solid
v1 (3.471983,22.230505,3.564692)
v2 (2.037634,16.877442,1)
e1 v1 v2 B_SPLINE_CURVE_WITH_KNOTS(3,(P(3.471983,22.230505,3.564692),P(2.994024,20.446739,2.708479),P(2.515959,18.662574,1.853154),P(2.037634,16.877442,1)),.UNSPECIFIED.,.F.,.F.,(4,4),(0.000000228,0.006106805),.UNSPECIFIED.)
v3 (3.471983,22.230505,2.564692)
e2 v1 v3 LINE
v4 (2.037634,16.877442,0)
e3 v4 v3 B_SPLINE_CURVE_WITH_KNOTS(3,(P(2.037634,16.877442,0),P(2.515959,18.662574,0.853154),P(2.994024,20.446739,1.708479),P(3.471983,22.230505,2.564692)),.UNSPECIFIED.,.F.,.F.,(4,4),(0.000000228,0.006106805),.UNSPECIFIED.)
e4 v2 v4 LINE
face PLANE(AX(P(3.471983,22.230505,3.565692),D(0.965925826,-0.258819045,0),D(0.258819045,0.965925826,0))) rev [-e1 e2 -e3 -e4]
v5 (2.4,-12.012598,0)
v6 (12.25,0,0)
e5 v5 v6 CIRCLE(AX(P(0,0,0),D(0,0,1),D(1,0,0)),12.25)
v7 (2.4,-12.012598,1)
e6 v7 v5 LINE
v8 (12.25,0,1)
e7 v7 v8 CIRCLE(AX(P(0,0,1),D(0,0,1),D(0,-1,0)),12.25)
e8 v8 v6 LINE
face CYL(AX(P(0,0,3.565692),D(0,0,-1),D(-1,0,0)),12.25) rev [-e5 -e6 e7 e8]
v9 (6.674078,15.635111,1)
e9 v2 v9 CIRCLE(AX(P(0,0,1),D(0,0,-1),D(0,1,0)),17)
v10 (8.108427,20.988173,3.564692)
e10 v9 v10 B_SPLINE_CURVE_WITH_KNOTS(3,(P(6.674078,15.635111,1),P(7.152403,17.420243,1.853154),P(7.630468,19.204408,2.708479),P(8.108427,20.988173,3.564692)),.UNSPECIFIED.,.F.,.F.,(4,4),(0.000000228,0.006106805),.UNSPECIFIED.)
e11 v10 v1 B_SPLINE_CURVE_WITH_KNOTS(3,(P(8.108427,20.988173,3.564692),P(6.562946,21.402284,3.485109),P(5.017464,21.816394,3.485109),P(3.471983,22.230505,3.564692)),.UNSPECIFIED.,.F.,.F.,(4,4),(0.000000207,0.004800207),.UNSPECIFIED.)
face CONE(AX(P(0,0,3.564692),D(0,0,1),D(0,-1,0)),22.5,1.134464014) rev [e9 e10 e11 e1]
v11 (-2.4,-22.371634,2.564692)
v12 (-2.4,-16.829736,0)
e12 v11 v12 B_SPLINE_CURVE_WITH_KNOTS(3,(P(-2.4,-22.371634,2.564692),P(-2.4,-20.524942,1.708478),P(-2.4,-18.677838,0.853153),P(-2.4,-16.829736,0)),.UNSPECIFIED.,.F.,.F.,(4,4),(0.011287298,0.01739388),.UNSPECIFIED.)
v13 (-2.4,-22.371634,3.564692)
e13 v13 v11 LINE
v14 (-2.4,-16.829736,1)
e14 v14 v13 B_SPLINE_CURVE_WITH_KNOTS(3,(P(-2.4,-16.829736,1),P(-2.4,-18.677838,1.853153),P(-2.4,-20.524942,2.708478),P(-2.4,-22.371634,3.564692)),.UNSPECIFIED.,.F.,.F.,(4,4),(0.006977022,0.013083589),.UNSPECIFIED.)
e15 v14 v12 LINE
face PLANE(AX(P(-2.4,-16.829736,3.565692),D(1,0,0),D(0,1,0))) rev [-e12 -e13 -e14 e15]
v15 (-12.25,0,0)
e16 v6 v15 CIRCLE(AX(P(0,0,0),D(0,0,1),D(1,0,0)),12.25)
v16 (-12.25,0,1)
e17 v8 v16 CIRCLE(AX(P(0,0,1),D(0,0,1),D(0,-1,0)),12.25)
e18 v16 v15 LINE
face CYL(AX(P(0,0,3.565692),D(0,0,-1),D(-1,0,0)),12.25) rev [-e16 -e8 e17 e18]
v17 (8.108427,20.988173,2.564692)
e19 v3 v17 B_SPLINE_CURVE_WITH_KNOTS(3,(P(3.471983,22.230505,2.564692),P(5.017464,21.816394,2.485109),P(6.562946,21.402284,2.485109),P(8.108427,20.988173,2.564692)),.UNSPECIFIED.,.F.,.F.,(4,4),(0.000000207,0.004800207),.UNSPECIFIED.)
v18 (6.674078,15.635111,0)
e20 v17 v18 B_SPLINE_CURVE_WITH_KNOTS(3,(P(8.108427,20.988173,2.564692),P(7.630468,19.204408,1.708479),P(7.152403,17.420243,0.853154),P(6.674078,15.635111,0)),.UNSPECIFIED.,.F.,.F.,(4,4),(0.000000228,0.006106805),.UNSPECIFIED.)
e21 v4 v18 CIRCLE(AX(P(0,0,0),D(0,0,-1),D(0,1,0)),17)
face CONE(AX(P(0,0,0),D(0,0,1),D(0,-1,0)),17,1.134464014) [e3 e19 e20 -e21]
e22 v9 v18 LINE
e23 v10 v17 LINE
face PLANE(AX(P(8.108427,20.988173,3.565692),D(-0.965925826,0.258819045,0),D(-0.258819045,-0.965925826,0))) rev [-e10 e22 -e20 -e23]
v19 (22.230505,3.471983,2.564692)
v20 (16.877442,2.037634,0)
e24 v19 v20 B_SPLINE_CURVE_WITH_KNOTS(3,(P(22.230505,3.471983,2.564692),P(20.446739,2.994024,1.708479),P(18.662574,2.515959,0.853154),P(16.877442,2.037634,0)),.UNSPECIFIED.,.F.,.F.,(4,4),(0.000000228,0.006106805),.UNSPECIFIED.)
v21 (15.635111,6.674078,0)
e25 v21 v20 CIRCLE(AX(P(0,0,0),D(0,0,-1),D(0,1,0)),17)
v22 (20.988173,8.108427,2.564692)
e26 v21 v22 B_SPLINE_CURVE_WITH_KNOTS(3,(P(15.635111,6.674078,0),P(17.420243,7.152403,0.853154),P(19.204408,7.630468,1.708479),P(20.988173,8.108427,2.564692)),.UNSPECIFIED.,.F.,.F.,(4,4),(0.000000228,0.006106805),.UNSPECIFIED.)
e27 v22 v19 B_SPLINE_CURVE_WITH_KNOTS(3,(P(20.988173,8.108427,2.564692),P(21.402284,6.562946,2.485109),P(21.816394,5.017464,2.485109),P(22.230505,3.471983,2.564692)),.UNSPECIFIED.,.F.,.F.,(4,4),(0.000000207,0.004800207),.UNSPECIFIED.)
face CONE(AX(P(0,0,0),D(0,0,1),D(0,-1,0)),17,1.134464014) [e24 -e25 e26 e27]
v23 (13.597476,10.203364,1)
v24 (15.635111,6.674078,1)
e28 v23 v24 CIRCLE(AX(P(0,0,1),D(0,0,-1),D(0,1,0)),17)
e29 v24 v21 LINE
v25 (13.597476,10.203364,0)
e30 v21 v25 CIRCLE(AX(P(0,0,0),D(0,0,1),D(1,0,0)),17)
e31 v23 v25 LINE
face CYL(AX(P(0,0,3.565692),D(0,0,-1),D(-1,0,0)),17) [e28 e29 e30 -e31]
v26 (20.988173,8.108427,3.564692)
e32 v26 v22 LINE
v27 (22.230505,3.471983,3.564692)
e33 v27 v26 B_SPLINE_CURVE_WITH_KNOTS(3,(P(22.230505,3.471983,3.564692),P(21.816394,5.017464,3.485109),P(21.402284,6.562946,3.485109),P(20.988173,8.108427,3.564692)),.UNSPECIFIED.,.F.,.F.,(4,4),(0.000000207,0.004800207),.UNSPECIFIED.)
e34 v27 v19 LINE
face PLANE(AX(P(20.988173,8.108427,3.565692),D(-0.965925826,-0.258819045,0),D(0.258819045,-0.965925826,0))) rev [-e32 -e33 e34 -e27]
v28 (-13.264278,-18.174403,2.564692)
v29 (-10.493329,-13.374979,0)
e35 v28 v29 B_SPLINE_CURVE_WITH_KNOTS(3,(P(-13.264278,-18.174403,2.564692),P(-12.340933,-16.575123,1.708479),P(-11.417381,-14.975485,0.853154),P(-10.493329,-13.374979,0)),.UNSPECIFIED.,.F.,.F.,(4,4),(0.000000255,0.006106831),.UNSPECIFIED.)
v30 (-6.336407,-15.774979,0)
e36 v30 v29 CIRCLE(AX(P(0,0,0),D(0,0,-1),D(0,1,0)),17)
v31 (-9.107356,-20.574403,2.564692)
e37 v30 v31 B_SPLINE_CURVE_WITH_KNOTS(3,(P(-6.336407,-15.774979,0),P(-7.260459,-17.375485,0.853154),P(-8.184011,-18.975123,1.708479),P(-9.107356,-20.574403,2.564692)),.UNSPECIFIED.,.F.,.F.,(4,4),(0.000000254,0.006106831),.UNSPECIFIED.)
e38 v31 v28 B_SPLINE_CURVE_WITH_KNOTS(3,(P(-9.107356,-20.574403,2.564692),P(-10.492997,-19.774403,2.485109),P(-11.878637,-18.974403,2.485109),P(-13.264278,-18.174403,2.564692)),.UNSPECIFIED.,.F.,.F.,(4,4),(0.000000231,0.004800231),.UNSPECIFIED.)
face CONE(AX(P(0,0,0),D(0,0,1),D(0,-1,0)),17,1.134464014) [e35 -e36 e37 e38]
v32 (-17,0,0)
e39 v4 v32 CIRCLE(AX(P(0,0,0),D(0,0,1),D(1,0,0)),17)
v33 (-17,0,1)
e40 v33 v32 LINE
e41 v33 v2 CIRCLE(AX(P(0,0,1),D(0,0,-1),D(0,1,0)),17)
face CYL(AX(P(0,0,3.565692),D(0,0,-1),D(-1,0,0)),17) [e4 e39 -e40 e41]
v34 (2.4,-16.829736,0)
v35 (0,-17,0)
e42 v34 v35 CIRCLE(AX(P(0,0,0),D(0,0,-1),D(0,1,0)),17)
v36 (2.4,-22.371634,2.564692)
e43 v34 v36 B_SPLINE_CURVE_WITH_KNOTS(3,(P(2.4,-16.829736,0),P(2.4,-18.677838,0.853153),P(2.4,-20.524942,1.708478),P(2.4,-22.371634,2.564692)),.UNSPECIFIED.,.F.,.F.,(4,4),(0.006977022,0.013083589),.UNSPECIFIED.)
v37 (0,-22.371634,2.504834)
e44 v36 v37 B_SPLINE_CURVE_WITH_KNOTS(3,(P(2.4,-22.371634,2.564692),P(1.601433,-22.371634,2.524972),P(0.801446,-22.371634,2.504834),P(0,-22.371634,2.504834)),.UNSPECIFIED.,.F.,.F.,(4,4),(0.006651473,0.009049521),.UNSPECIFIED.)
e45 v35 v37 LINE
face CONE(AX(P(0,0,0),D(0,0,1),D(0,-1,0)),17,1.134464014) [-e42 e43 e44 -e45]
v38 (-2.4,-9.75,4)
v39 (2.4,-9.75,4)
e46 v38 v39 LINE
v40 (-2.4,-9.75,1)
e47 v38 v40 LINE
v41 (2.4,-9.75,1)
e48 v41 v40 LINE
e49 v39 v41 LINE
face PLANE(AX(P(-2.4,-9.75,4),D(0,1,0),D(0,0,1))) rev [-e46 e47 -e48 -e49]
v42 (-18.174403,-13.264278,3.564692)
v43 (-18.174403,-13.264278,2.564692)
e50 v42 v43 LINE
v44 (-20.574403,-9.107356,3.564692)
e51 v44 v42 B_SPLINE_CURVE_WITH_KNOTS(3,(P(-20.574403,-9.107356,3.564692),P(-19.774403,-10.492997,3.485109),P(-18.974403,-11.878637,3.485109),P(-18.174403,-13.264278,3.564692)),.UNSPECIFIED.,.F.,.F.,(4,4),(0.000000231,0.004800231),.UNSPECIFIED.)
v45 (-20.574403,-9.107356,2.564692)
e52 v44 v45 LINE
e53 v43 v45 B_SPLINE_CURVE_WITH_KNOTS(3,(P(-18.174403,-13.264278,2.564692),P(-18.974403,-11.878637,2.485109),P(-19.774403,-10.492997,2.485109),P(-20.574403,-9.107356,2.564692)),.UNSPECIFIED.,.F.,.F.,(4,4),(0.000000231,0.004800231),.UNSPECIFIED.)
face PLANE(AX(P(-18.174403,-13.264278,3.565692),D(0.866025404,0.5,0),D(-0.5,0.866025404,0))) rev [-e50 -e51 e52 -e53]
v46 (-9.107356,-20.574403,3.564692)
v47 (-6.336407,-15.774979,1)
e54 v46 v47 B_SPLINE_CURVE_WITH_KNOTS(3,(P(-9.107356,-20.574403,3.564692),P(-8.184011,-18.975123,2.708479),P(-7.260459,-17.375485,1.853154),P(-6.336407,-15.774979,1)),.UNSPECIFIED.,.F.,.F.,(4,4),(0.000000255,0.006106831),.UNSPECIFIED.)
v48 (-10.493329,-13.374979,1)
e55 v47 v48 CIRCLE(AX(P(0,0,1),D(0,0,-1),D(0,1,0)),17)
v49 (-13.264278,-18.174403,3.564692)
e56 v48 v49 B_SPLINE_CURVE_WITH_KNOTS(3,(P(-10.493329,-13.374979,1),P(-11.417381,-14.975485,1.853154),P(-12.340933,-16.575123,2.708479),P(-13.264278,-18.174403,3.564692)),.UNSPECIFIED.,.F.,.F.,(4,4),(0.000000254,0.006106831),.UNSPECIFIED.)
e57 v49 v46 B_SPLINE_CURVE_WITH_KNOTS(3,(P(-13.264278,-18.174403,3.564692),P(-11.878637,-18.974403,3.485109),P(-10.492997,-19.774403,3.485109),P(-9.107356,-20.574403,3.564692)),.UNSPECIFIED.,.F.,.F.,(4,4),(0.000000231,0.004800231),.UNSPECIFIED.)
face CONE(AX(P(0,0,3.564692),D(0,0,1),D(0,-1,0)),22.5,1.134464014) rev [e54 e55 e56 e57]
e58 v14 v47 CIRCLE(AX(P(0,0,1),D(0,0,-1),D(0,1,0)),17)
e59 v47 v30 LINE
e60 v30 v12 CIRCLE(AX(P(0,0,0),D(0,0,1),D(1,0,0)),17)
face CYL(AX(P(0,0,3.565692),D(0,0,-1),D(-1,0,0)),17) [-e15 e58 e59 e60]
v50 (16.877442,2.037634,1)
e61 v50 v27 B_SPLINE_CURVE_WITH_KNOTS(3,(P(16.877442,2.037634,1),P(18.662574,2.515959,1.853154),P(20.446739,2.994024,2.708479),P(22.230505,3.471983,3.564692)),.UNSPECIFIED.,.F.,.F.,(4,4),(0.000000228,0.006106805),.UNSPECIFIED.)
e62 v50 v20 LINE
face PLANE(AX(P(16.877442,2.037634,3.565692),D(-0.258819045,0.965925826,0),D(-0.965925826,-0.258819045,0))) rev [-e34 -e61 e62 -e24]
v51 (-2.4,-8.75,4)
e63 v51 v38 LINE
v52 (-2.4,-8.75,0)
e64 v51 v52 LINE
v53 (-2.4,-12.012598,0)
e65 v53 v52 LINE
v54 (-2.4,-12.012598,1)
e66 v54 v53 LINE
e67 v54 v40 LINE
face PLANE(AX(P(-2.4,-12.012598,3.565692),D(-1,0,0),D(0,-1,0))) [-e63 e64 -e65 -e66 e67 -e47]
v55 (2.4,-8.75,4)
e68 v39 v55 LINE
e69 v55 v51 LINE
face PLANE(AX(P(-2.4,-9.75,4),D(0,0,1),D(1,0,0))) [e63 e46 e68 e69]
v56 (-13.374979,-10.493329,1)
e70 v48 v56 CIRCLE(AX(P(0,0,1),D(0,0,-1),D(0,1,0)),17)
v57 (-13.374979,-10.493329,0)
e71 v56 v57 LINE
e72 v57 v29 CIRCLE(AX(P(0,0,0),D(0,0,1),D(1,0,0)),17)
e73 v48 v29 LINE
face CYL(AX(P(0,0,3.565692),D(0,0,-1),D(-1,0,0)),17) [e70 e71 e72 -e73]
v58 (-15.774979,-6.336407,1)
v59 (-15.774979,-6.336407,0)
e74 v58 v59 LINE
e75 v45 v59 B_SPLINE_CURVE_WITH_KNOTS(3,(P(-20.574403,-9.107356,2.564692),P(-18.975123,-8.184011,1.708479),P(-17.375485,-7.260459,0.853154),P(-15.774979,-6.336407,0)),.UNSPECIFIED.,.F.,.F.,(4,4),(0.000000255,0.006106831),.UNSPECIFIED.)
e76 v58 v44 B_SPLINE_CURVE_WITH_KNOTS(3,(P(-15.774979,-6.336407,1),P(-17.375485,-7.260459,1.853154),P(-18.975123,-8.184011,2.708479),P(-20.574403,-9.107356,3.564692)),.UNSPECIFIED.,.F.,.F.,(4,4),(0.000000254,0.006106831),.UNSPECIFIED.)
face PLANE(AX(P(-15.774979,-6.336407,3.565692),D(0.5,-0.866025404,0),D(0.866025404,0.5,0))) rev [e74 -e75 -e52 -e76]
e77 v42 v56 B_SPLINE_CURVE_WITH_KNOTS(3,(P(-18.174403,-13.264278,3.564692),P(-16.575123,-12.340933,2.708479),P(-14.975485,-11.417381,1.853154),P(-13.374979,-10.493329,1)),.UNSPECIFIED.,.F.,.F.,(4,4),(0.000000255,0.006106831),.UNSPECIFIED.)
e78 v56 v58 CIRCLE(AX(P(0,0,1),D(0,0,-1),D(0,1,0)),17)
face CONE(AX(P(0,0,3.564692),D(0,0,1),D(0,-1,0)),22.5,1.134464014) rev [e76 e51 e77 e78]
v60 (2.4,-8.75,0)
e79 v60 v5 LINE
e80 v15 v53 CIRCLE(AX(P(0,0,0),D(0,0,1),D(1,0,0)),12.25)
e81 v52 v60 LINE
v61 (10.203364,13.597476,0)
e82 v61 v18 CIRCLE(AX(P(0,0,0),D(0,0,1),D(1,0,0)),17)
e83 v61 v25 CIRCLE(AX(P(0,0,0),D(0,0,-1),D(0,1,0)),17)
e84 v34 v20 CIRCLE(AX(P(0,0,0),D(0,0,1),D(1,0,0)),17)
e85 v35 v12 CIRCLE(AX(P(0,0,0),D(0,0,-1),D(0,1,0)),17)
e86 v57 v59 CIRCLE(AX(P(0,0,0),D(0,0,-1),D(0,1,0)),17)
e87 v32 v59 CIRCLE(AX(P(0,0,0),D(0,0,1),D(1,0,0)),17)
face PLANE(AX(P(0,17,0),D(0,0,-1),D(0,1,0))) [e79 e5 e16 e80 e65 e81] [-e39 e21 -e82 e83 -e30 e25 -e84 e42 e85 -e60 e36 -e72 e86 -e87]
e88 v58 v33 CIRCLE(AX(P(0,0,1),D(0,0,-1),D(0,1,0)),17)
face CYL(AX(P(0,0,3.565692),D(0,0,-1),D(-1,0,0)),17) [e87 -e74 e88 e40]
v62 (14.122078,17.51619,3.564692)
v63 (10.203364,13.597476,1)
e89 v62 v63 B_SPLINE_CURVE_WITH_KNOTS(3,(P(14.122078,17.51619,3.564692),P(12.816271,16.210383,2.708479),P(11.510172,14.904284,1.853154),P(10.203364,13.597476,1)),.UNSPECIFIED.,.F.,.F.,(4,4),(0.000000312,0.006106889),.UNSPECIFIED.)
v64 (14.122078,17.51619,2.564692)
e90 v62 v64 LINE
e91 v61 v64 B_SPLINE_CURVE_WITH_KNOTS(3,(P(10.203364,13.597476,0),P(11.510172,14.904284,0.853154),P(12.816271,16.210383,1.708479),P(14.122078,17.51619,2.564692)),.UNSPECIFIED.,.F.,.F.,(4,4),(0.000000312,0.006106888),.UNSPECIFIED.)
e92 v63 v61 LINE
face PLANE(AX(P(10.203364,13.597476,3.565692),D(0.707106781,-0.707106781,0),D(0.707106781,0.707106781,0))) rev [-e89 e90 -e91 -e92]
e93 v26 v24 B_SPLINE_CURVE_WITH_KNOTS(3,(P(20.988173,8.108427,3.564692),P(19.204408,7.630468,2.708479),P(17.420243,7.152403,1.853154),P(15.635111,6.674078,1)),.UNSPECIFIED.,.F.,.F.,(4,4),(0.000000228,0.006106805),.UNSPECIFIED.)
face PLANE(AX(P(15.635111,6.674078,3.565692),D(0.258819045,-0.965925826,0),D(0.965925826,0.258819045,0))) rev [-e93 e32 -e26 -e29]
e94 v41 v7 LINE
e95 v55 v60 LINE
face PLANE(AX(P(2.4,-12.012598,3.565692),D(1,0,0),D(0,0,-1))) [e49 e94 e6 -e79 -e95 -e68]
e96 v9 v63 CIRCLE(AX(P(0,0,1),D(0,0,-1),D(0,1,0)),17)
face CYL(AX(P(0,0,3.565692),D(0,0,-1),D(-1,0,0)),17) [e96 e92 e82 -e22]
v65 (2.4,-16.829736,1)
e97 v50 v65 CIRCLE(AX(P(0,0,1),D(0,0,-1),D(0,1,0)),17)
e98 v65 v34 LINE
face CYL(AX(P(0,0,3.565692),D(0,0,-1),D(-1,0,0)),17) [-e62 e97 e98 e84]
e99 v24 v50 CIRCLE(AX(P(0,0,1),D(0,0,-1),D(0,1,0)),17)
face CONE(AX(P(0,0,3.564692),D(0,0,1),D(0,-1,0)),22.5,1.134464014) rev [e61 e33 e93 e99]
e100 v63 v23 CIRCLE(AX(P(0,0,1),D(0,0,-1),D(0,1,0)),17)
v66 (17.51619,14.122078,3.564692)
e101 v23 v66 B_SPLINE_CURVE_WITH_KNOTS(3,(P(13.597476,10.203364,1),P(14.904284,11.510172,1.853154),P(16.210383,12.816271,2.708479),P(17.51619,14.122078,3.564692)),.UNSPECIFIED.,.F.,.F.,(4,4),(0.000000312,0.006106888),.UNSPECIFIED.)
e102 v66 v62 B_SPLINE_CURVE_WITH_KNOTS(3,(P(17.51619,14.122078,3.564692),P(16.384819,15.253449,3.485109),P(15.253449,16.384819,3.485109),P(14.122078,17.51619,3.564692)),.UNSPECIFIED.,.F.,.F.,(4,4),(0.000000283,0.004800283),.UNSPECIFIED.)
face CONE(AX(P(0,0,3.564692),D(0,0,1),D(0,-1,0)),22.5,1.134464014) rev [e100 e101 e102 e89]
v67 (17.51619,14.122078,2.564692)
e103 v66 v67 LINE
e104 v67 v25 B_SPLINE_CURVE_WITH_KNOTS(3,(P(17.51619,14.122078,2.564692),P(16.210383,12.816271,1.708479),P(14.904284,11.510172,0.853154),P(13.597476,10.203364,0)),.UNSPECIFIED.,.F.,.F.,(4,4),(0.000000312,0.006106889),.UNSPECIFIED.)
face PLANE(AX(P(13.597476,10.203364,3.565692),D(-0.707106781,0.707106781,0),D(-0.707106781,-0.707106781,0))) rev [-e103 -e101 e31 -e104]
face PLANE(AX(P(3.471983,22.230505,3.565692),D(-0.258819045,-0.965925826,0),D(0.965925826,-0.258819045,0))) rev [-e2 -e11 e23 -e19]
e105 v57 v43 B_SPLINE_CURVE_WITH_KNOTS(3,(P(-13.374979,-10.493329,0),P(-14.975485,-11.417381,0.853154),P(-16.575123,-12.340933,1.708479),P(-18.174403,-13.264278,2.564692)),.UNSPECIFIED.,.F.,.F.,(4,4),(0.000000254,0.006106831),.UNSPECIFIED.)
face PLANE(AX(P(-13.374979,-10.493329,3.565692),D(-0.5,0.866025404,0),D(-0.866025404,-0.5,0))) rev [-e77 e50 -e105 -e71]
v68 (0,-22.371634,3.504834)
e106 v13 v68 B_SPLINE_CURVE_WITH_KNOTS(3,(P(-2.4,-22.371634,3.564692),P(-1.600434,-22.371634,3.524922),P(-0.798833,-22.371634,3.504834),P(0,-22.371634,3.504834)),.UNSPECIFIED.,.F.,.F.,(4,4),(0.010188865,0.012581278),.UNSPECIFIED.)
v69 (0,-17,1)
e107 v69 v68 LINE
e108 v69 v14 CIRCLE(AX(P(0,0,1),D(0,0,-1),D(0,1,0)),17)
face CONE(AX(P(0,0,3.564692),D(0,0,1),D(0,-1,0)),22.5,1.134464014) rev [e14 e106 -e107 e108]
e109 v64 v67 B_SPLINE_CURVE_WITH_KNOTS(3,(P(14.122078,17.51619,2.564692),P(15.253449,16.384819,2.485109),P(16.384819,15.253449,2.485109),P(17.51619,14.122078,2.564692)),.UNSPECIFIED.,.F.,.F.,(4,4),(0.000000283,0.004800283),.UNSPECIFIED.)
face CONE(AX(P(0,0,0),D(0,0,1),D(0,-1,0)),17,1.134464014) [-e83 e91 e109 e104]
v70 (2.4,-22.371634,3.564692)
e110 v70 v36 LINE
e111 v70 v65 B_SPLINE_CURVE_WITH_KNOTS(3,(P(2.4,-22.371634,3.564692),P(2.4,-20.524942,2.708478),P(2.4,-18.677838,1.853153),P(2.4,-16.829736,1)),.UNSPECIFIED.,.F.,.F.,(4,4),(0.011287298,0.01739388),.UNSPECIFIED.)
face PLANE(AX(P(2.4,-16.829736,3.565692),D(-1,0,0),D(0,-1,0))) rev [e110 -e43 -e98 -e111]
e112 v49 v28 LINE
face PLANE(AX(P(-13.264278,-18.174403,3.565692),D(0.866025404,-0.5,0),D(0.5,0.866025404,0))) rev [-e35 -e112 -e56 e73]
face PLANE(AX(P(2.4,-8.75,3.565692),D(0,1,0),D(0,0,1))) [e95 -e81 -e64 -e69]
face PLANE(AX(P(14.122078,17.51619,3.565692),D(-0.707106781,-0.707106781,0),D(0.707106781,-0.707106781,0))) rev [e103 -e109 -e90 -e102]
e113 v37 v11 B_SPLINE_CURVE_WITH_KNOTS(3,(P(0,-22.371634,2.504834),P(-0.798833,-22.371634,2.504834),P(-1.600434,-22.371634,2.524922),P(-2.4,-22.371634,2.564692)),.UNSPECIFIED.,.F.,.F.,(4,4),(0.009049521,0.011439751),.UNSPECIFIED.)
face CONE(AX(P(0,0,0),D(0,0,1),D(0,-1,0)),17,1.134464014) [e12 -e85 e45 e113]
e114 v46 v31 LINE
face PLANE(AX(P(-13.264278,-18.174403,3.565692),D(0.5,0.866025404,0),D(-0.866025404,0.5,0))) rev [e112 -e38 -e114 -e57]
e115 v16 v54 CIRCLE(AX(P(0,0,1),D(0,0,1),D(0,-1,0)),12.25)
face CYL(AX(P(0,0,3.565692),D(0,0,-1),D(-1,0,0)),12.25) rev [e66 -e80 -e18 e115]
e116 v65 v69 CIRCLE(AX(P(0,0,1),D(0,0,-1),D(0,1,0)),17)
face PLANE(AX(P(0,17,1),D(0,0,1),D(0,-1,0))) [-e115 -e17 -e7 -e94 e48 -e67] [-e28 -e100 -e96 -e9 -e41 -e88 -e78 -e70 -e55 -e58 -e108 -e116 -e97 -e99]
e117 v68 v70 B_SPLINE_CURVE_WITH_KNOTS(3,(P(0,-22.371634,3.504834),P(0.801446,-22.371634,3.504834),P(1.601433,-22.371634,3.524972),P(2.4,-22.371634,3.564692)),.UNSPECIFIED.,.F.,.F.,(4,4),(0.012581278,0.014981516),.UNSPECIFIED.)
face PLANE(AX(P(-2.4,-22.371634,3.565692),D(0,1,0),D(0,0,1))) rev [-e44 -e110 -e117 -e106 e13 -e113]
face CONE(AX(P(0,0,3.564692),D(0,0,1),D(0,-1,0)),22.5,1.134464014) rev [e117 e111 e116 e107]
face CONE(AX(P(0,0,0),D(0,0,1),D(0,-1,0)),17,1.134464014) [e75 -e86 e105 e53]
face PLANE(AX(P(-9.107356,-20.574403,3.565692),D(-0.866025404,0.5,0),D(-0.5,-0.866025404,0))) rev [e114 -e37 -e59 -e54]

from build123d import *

# Parameters (mm, degrees)
CUT_EXTRUDE2_START  = -3e-06
SKETCH3_OUTSIDE_W   = 59.748
SKETCH3_OUTSIDE_H   = 59.748
CUT_EXTRUDE2_DEPTH  = 3.564697
SKETCH4_W           = 4.8
SKETCH4_H           = 1
BOSS_EXTRUDE1_DEPTH = 4


with BuildPart() as part:
    # Sketch2 → Boss-Revolve (revolve)
    with BuildSketch(Plane(origin=(0, 0, 0), x_dir=(0, 0, -1), z_dir=(1, 0, 0))):
        Polygon((-2.56469212, 22.5), (0, 17), (0, 0), (-1, 0), (-1, 17), (-3.56469212, 22.5), align=None)
    revolve(axis=Axis((0, 0, 0), (0, 0, 1)))

    # Sketch3 outside → Cut-Extrude2 (cut)
    # profile 1 of 2: a face of its own
    with BuildSketch(Plane.XY.offset(CUT_EXTRUDE2_START)):
        Rectangle(SKETCH3_OUTSIDE_W, SKETCH3_OUTSIDE_H)
        with BuildLine():
            Line((-2.4, -16.829735589), (-2.4, -22.371633825))
            Line((-2.4, -22.371633825), (2.4, -22.371633825))
            Line((2.4, -22.371633825), (2.4, -16.829735589))
            ThreePointArc((2.4, -16.829735589), (13.487006785, -10.348944293), (16.877441963, 2.037634111))
            Line((16.877441963, 2.037634111), (22.230504596, 3.471982921))
            Line((22.230504596, 3.471982921), (20.98817318, 8.108426887))
            Line((20.98817318, 8.108426887), (15.635110547, 6.674078078))
            ThreePointArc((15.635110547, 6.674078078), (14.722431864, 8.5), (13.597476435, 10.203363886))
            Line((13.597476435, 10.203363886), (17.516190259, 14.122077709))
            Line((17.516190259, 14.122077709), (14.122077709, 17.516190259))
            Line((14.122077709, 17.516190259), (10.203363886, 13.597476435))
            ThreePointArc((10.203363886, 13.597476435), (8.5, 14.722431864), (6.674078078, 15.635110547))
            Line((6.674078078, 15.635110547), (8.108426887, 20.98817318))
            Line((8.108426887, 20.98817318), (3.471982921, 22.230504596))
            Line((3.471982921, 22.230504596), (2.037634111, 16.877441963))
            ThreePointArc((2.037634111, 16.877441963), (-13.487006785, 10.348944293), (-15.774978559, -6.336406825))
            Line((-15.774978559, -6.336406825), (-20.574403217, -9.107355943))
            Line((-20.574403217, -9.107355943), (-18.174403217, -13.264277882))
            Line((-18.174403217, -13.264277882), (-13.374978559, -10.493328764))
            ThreePointArc((-13.374978559, -10.493328764), (-12.02081528, -12.02081528), (-10.493328764, -13.374978559))
            Line((-10.493328764, -13.374978559), (-13.264277882, -18.174403217))
            Line((-13.264277882, -18.174403217), (-9.107355943, -20.574403217))
            Line((-9.107355943, -20.574403217), (-6.336406825, -15.774978559))
            ThreePointArc((-6.336406825, -15.774978559), (-4.399923767, -16.420739047), (-2.4, -16.829735589))
        make_face(mode=Mode.SUBTRACT)
    # profile 2 of 2: a face of its own
    with BuildSketch(Plane.XY.offset(CUT_EXTRUDE2_START)):
        with BuildLine():
            Line((2.4, -12.012597554), (2.4, -8.75))
            Line((2.4, -8.75), (-2.4, -8.75))
            Line((-2.4, -8.75), (-2.4, -12.012597554))
            ThreePointArc((-2.4, -12.012597554), (0, 12.25), (2.4, -12.012597554))
        make_face()
    extrude(amount=CUT_EXTRUDE2_DEPTH, mode=Mode.SUBTRACT)

    # Sketch4 → Boss-Extrude1 (add)
    with BuildSketch(Plane.XY):
        with Locations((0, -9.25)):
            Rectangle(SKETCH4_W, SKETCH4_H)
    extrude(amount=BOSS_EXTRUDE1_DEPTH)


solid = part.part
